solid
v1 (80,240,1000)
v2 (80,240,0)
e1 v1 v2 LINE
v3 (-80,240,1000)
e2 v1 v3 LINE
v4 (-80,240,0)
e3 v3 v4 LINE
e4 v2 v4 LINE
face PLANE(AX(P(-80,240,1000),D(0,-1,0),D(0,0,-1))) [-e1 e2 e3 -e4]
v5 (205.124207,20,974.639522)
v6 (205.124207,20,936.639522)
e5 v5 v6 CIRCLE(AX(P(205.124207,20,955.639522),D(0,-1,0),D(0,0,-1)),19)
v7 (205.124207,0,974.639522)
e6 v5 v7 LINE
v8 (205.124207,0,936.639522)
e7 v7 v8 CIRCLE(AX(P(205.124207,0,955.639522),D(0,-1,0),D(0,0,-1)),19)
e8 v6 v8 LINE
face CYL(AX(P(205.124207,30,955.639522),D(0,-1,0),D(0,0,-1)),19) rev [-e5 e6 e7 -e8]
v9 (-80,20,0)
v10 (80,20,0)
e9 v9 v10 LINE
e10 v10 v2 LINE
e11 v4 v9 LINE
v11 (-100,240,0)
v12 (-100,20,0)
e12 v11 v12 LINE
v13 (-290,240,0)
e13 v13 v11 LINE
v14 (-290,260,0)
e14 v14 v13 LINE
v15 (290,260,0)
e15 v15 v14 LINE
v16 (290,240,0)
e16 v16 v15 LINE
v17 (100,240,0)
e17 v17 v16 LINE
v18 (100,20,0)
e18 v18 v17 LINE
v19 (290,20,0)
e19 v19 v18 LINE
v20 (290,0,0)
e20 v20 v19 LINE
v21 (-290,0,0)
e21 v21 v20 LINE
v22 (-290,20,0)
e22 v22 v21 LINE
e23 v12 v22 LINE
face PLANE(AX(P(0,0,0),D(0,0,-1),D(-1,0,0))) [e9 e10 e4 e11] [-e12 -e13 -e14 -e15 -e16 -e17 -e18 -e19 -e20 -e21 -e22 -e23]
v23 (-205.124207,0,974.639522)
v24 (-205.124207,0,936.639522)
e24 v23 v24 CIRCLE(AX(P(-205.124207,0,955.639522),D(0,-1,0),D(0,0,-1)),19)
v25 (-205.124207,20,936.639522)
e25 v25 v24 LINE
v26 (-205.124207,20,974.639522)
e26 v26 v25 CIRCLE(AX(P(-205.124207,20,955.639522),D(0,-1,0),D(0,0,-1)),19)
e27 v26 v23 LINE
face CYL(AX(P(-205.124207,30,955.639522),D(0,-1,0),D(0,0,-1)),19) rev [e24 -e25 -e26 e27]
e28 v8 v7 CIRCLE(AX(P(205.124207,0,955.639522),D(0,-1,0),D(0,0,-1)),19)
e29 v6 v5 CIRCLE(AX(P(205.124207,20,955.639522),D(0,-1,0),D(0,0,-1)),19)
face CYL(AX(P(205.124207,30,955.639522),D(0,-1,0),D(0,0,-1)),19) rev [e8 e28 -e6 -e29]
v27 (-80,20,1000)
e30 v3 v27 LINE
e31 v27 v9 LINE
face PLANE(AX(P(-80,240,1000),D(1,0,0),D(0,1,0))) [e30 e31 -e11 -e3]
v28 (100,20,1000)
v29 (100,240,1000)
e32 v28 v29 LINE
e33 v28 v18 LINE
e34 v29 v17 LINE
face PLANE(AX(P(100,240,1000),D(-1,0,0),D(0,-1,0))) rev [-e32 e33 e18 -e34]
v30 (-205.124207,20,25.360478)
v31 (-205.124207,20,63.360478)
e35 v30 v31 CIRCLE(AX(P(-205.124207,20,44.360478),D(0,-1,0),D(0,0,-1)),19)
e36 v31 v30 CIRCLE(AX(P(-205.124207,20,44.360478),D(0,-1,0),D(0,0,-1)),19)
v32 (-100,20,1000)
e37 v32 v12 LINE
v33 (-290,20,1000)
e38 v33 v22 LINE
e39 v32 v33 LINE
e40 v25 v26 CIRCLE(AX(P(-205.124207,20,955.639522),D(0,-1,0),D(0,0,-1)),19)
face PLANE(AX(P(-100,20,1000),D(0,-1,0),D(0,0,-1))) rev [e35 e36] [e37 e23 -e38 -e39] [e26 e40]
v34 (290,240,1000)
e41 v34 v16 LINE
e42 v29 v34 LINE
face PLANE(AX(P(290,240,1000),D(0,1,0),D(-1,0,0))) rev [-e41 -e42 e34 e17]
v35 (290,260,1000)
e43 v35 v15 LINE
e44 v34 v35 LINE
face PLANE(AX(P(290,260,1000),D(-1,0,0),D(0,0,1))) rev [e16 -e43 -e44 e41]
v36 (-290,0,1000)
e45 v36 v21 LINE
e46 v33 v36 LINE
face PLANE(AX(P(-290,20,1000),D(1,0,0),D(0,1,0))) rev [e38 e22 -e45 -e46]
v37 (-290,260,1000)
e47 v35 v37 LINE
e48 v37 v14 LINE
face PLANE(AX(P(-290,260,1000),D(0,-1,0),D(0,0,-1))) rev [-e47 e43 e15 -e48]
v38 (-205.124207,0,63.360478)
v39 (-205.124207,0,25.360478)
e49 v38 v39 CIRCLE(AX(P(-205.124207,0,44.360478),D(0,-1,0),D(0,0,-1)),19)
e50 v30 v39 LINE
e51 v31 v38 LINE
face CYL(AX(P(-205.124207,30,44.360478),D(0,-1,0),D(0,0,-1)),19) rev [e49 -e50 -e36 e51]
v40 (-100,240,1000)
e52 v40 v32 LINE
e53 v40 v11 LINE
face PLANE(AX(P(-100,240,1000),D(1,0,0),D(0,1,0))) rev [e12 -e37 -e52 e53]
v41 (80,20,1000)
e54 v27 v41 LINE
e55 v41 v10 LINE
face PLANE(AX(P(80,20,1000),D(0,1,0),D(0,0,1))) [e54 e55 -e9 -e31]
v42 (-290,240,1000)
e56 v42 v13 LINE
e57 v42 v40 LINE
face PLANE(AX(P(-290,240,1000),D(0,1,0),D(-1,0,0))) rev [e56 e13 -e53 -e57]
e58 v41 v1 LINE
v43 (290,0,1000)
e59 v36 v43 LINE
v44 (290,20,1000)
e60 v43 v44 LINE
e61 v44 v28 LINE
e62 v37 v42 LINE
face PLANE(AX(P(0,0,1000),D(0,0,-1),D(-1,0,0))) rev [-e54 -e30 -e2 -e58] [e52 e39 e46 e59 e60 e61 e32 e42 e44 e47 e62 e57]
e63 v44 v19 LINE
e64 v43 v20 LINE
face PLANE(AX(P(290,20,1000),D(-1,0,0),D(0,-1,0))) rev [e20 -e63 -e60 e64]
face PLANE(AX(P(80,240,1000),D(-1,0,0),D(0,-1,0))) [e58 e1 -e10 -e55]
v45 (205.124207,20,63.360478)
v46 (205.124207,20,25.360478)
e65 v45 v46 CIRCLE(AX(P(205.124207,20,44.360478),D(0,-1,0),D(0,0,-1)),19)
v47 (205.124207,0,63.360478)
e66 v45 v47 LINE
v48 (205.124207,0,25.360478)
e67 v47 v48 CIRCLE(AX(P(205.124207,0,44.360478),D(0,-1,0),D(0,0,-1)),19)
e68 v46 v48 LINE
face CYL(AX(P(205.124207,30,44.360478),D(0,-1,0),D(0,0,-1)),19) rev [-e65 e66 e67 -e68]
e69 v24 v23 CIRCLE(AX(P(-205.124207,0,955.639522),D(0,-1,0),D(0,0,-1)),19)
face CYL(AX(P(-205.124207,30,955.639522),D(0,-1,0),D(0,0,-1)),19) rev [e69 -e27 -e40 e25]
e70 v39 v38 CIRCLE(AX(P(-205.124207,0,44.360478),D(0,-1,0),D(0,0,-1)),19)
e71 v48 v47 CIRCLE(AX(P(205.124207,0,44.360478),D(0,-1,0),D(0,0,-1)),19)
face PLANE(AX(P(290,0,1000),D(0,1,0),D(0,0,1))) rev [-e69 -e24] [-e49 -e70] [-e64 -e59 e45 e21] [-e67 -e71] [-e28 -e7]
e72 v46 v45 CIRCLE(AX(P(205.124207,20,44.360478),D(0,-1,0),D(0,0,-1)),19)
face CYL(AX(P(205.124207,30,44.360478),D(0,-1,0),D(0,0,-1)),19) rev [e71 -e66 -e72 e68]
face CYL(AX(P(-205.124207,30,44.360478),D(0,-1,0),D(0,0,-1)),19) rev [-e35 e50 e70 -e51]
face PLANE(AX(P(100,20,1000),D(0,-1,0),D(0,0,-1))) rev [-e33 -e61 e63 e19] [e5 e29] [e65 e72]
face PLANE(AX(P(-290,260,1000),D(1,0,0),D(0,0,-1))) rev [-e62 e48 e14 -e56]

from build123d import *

# Parameters (mm, degrees)
SKETCH1_W           = 160
SKETCH1_H           = 220
BOSS_EXTRUDE1_DEPTH = 1000
SKETCH2_R           = 19
CUT_EXTRUDE1_DEPTH  = 30


with BuildPart() as part:
    # Sketch1 → Boss-Extrude1 (new body)
    with BuildSketch(Plane.XY):
        Polygon((-290, 260), (290, 260), (290, 240), (100, 240), (100, 20), (290, 20), (290, 0), (-290, 0), (-290, 20), (-100, 20), (-100, 240), (-290, 240), align=None)
        with Locations((0, 130)):
            Rectangle(SKETCH1_W, SKETCH1_H, mode=Mode.SUBTRACT)
    extrude(amount=BOSS_EXTRUDE1_DEPTH)

    # Sketch2 → Cut-Extrude1 (cut)
    with BuildSketch(Plane(origin=(0, 0, 0), x_dir=(-1, 0, 0), z_dir=(0, -1, 0))):
        with Locations(Location((205.124206689, -955.639521656, 0), (0, 0, 90))):
            Circle(SKETCH2_R)
        with Locations(Location((-205.124206689, -955.639521656, 0), (0, 0, 90))):
            Circle(SKETCH2_R)
        with Locations(Location((-205.124206689, -44.360478344, 0), (0, 0, 90))):
            Circle(SKETCH2_R)
        with Locations(Location((205.124206689, -44.360478344, 0), (0, 0, 90))):
            Circle(SKETCH2_R)
    extrude(amount=-CUT_EXTRUDE1_DEPTH, mode=Mode.SUBTRACT)


solid = part.part
